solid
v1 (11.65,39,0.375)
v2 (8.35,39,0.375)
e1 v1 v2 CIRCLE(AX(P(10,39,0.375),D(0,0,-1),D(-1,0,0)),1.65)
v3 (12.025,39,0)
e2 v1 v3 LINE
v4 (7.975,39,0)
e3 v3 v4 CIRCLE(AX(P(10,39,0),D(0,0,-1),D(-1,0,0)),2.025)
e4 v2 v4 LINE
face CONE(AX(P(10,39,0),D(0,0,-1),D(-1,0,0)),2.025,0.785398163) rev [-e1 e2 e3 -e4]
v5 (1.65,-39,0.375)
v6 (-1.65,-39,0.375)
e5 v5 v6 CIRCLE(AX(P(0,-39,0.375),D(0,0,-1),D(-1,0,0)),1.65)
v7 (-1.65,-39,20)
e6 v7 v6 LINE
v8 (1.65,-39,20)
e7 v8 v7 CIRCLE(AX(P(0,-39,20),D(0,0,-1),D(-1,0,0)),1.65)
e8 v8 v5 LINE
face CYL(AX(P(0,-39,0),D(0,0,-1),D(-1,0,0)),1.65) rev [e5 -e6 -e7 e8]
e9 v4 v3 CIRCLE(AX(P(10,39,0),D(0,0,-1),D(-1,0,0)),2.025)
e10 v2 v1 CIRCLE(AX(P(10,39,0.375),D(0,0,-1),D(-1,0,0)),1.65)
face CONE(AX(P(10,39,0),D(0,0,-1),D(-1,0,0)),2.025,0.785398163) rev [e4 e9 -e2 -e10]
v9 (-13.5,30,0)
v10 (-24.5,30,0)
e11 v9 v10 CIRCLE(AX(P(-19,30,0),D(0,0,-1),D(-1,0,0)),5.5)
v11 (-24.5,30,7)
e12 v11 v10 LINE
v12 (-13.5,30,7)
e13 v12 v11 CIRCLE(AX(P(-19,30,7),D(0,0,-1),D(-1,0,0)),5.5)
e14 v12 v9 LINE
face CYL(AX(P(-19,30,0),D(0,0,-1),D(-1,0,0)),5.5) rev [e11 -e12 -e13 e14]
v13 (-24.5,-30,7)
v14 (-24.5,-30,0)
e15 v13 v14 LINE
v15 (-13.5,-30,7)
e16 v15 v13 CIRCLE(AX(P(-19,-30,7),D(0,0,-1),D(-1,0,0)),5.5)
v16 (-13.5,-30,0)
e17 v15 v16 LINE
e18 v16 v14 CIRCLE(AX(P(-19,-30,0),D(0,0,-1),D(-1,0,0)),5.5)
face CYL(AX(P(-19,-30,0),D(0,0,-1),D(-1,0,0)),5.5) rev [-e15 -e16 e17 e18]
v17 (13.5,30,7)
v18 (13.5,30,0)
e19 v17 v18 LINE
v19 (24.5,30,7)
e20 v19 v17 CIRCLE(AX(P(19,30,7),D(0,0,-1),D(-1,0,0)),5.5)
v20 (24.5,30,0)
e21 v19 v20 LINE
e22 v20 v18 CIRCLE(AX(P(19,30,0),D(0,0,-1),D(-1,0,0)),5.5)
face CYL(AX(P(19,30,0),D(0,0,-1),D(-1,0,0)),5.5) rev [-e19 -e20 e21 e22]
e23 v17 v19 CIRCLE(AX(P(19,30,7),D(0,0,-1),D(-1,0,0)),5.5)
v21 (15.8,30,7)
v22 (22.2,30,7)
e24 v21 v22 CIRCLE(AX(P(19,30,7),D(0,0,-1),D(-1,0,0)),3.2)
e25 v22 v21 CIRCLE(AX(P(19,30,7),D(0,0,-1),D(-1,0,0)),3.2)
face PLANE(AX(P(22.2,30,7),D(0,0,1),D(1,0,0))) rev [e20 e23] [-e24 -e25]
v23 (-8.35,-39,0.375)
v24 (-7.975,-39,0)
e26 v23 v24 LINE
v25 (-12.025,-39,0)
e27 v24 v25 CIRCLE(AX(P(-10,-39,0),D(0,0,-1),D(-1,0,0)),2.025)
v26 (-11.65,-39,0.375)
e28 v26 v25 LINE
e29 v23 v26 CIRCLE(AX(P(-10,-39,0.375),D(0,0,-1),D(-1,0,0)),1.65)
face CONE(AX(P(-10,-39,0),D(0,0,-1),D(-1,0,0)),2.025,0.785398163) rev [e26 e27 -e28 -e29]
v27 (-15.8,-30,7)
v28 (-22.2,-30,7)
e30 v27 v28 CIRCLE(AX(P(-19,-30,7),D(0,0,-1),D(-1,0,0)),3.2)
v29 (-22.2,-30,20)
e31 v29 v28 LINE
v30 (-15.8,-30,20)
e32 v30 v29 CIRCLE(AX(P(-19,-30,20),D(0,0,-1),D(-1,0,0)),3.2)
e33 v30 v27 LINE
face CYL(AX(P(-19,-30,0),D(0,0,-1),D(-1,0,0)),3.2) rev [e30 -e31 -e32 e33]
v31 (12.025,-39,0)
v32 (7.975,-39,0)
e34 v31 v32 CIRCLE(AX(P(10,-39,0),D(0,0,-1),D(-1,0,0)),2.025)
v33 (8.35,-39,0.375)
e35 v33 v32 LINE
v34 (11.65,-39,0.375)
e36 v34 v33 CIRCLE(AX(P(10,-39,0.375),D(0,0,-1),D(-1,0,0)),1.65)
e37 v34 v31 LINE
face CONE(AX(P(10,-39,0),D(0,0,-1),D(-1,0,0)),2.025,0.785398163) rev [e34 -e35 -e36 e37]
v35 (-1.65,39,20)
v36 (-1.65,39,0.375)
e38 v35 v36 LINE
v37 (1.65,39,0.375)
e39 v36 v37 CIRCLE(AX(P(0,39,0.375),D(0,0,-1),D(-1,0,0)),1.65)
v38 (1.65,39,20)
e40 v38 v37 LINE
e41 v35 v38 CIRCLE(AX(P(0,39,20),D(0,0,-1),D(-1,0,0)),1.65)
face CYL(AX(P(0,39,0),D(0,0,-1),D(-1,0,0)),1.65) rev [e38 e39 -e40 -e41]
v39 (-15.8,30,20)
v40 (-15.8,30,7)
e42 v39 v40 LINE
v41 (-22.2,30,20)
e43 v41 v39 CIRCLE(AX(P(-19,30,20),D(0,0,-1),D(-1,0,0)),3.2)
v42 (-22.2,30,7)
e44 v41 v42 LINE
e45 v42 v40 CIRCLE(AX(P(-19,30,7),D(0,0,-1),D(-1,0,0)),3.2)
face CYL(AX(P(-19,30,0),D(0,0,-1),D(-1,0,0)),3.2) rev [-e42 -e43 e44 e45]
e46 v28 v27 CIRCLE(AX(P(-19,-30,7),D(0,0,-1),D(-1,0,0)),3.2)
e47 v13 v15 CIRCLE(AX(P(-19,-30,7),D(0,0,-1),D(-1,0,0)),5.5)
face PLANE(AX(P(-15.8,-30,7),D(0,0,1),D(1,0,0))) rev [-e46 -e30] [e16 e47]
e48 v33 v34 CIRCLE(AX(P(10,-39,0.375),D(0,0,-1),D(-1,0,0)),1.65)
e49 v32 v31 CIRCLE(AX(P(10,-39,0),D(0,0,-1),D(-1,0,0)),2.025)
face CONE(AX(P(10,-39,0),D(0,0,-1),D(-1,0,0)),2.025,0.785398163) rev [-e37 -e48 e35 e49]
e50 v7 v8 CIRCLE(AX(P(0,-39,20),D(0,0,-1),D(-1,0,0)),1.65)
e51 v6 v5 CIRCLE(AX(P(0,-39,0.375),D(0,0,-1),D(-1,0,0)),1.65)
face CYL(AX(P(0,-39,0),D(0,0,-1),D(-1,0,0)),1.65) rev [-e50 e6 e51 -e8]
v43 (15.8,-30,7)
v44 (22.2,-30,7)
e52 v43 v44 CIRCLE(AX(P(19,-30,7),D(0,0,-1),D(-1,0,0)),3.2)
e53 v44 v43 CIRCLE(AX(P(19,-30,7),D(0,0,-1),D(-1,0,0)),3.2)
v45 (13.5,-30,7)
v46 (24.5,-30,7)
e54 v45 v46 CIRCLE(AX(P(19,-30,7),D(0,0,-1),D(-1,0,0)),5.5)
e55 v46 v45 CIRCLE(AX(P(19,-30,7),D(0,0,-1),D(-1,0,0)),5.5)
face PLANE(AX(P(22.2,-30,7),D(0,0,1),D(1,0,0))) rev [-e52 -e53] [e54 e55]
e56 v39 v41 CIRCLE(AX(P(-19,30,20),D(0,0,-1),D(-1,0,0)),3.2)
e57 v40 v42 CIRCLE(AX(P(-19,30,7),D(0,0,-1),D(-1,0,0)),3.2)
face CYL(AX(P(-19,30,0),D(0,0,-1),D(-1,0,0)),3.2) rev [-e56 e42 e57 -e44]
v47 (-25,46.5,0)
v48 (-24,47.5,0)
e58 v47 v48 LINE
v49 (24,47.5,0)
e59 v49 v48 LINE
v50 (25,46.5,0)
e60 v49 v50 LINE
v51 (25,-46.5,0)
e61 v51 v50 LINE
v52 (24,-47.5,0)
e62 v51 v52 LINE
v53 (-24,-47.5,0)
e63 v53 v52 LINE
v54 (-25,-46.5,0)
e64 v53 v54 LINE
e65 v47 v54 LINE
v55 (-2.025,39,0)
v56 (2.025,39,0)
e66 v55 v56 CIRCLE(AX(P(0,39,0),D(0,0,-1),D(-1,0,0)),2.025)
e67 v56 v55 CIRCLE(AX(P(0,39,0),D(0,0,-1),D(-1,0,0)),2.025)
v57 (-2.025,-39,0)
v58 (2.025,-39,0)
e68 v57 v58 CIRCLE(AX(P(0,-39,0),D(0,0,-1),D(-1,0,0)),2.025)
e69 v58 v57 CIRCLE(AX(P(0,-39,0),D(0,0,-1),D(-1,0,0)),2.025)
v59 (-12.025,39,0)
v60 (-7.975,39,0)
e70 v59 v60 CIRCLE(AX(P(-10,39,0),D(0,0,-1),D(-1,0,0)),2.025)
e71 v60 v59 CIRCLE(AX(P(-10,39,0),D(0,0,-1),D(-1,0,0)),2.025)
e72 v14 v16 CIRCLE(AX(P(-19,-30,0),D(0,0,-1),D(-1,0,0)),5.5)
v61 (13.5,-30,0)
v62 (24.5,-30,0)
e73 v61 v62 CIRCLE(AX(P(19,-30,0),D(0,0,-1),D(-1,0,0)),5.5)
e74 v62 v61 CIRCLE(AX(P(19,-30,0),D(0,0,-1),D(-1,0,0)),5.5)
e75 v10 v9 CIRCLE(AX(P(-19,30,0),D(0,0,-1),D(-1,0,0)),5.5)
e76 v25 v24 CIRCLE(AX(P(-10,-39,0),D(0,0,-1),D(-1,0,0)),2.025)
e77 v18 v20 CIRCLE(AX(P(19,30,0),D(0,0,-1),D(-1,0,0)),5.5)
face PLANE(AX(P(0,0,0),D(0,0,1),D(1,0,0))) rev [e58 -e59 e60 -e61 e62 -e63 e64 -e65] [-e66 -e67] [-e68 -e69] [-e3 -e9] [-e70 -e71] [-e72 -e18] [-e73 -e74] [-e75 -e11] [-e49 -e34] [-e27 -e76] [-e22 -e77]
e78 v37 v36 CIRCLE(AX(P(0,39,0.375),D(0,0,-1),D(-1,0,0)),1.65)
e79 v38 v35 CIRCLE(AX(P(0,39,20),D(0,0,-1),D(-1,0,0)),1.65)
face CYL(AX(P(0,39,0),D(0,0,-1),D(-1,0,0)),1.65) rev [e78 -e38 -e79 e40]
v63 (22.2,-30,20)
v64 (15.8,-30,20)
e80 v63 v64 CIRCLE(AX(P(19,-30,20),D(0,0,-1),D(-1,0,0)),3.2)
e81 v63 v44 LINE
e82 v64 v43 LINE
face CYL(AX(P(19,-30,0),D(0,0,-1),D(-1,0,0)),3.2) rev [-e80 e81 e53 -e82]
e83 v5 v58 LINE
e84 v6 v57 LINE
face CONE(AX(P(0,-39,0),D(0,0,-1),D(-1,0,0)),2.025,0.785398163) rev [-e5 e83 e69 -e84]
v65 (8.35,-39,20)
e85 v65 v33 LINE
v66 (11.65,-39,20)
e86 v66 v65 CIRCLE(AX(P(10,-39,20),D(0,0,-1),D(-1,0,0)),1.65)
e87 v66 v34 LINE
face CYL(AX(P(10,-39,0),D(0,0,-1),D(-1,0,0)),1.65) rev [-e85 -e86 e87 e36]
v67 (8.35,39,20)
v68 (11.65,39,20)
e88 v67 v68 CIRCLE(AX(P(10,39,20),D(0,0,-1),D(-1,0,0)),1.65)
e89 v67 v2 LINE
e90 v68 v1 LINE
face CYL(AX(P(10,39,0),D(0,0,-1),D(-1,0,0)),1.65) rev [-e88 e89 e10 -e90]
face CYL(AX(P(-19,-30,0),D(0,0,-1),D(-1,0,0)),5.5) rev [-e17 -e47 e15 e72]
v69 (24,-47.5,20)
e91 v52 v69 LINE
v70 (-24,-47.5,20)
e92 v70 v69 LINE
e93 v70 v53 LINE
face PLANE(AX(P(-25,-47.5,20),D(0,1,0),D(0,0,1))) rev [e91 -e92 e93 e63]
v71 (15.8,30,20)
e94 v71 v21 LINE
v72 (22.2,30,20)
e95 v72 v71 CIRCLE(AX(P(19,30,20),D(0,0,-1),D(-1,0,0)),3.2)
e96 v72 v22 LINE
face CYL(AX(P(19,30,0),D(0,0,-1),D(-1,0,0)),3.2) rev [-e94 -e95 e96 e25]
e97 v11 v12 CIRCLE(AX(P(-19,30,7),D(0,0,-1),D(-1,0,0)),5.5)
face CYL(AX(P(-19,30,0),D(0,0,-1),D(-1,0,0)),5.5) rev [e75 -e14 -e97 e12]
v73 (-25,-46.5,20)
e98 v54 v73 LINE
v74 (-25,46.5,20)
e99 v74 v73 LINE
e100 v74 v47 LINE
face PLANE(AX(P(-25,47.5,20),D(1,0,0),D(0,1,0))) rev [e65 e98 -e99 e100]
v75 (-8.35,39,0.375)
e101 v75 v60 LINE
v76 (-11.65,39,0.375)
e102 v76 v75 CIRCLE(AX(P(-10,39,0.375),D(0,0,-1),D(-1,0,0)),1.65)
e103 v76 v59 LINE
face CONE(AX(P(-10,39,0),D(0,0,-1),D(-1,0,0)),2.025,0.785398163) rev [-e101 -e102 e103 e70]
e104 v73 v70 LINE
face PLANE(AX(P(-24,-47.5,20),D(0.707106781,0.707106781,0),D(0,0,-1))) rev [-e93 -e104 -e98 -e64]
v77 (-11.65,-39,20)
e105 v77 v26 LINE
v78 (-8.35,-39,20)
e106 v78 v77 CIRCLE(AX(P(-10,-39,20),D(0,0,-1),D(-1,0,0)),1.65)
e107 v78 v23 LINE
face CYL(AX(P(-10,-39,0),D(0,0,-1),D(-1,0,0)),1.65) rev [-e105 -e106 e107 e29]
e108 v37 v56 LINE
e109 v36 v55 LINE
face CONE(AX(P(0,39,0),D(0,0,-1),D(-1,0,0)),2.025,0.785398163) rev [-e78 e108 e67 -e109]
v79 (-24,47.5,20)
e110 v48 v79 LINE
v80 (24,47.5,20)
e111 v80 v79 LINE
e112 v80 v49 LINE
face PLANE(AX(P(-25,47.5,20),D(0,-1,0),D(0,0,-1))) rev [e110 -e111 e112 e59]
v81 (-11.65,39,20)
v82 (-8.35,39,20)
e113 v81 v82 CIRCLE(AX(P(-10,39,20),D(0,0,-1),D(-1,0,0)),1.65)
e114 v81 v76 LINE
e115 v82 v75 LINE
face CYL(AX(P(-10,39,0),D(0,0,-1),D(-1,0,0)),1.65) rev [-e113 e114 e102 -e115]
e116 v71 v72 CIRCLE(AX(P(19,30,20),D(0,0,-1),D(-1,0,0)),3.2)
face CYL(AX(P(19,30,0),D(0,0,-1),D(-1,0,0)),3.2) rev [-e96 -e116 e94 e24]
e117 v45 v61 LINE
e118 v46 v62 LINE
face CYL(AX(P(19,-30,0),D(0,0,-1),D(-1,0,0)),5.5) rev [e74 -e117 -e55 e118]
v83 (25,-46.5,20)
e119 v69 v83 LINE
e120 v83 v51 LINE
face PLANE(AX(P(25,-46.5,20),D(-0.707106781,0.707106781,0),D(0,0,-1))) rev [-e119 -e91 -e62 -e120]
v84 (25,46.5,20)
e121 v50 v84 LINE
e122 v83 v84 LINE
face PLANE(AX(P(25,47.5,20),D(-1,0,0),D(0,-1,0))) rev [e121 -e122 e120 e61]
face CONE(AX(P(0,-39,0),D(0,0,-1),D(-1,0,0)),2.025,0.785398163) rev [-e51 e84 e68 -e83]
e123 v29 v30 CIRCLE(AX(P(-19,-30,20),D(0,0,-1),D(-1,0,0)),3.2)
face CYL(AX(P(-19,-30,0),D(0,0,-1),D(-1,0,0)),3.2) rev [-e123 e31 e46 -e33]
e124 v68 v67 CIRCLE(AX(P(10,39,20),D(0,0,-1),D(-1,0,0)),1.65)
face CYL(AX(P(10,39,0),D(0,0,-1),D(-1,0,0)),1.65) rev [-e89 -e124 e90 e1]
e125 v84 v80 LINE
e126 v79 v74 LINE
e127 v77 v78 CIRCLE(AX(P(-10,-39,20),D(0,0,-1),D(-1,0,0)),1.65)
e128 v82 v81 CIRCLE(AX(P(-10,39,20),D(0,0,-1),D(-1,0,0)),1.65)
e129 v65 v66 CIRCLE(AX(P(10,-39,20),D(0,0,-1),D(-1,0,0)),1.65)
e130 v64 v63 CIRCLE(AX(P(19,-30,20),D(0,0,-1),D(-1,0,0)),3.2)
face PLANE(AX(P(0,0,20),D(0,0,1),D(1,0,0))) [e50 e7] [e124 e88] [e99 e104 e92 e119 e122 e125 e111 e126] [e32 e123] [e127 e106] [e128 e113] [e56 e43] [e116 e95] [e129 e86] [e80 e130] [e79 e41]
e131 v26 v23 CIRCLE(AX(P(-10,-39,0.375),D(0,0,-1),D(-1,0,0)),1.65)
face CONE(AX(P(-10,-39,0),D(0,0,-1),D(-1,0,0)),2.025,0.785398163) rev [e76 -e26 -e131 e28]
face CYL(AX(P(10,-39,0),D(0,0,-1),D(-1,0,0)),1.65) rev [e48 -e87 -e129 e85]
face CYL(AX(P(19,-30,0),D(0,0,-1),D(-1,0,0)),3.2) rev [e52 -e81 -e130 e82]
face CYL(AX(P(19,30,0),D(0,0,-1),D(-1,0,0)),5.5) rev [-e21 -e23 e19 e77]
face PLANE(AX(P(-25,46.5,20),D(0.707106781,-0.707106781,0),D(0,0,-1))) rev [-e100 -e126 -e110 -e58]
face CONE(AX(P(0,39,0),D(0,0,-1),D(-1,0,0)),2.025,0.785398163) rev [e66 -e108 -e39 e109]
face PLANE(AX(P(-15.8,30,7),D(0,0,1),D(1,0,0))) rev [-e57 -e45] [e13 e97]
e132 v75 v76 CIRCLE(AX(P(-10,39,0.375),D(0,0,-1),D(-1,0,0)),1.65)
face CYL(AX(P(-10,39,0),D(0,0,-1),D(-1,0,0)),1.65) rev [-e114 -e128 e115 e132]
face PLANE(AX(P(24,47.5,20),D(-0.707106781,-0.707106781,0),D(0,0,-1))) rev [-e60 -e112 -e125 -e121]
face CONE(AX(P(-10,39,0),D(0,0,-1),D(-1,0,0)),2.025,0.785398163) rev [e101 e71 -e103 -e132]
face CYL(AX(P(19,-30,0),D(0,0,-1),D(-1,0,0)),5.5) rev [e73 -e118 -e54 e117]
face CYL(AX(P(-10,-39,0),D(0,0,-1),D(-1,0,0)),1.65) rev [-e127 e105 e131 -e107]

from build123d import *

# Parameters (mm, degrees)
SKETCH_1_W                   = 50
SKETCH_1_H                   = 95
EXTRUDE_1_DEPTH              = 20
HOLE_WIZARD_1_D              = 6.4
HOLE_WIZARD_1_CBORE_D        = 11
HOLE_WIZARD_1_CBORE_DEPTH    = 7
HOLE_WIZARD_M4_1_D           = 3.3
HOLE_WIZARD_M4_1_CSINK_D     = 4.05
HOLE_WIZARD_M4_1_CSINK_ANGLE = 90
CHAMFER_1_SIZE               = 1


with BuildPart() as part:
    # 草图1 → 凸台-拉伸1 (new body)
    with BuildSketch(Plane.XY):
        Rectangle(SKETCH_1_W, SKETCH_1_H)
    extrude(amount=EXTRUDE_1_DEPTH)

    # 打孔尺寸(%根据)内六角圆柱头螺钉的类型1 (through all)
    with Locations(Plane(origin=(0, 0, 0), x_dir=(-1, 0, 0), z_dir=(0, 0, -1))):
        with Locations((-19, 30), (-19, -30), (19, -30), (19, 30)):
            CounterBoreHole(HOLE_WIZARD_1_D / 2, HOLE_WIZARD_1_CBORE_D / 2, HOLE_WIZARD_1_CBORE_DEPTH)

    # M4 螺纹孔1 (through all)
    with Locations(Plane(origin=(0, 0, 0), x_dir=(-1, 0, 0), z_dir=(0, 0, -1))):
        with Locations((0, -39), (10, 39), (10, -39), (-10, -39), (-10, 39), (0, 39)):
            CounterSinkHole(HOLE_WIZARD_M4_1_D / 2, HOLE_WIZARD_M4_1_CSINK_D / 2, counter_sink_angle=HOLE_WIZARD_M4_1_CSINK_ANGLE)

    # 倒角1
    chamfer_1_edges = [part.edges().sort_by_distance(p)[0] for p in [
        (25, -47.5, 10),
        (-25, -47.5, 10),
        (-25, 47.5, 10),
        (25, 47.5, 10),
    ]]
    chamfer(chamfer_1_edges, length=CHAMFER_1_SIZE)


solid = part.part
